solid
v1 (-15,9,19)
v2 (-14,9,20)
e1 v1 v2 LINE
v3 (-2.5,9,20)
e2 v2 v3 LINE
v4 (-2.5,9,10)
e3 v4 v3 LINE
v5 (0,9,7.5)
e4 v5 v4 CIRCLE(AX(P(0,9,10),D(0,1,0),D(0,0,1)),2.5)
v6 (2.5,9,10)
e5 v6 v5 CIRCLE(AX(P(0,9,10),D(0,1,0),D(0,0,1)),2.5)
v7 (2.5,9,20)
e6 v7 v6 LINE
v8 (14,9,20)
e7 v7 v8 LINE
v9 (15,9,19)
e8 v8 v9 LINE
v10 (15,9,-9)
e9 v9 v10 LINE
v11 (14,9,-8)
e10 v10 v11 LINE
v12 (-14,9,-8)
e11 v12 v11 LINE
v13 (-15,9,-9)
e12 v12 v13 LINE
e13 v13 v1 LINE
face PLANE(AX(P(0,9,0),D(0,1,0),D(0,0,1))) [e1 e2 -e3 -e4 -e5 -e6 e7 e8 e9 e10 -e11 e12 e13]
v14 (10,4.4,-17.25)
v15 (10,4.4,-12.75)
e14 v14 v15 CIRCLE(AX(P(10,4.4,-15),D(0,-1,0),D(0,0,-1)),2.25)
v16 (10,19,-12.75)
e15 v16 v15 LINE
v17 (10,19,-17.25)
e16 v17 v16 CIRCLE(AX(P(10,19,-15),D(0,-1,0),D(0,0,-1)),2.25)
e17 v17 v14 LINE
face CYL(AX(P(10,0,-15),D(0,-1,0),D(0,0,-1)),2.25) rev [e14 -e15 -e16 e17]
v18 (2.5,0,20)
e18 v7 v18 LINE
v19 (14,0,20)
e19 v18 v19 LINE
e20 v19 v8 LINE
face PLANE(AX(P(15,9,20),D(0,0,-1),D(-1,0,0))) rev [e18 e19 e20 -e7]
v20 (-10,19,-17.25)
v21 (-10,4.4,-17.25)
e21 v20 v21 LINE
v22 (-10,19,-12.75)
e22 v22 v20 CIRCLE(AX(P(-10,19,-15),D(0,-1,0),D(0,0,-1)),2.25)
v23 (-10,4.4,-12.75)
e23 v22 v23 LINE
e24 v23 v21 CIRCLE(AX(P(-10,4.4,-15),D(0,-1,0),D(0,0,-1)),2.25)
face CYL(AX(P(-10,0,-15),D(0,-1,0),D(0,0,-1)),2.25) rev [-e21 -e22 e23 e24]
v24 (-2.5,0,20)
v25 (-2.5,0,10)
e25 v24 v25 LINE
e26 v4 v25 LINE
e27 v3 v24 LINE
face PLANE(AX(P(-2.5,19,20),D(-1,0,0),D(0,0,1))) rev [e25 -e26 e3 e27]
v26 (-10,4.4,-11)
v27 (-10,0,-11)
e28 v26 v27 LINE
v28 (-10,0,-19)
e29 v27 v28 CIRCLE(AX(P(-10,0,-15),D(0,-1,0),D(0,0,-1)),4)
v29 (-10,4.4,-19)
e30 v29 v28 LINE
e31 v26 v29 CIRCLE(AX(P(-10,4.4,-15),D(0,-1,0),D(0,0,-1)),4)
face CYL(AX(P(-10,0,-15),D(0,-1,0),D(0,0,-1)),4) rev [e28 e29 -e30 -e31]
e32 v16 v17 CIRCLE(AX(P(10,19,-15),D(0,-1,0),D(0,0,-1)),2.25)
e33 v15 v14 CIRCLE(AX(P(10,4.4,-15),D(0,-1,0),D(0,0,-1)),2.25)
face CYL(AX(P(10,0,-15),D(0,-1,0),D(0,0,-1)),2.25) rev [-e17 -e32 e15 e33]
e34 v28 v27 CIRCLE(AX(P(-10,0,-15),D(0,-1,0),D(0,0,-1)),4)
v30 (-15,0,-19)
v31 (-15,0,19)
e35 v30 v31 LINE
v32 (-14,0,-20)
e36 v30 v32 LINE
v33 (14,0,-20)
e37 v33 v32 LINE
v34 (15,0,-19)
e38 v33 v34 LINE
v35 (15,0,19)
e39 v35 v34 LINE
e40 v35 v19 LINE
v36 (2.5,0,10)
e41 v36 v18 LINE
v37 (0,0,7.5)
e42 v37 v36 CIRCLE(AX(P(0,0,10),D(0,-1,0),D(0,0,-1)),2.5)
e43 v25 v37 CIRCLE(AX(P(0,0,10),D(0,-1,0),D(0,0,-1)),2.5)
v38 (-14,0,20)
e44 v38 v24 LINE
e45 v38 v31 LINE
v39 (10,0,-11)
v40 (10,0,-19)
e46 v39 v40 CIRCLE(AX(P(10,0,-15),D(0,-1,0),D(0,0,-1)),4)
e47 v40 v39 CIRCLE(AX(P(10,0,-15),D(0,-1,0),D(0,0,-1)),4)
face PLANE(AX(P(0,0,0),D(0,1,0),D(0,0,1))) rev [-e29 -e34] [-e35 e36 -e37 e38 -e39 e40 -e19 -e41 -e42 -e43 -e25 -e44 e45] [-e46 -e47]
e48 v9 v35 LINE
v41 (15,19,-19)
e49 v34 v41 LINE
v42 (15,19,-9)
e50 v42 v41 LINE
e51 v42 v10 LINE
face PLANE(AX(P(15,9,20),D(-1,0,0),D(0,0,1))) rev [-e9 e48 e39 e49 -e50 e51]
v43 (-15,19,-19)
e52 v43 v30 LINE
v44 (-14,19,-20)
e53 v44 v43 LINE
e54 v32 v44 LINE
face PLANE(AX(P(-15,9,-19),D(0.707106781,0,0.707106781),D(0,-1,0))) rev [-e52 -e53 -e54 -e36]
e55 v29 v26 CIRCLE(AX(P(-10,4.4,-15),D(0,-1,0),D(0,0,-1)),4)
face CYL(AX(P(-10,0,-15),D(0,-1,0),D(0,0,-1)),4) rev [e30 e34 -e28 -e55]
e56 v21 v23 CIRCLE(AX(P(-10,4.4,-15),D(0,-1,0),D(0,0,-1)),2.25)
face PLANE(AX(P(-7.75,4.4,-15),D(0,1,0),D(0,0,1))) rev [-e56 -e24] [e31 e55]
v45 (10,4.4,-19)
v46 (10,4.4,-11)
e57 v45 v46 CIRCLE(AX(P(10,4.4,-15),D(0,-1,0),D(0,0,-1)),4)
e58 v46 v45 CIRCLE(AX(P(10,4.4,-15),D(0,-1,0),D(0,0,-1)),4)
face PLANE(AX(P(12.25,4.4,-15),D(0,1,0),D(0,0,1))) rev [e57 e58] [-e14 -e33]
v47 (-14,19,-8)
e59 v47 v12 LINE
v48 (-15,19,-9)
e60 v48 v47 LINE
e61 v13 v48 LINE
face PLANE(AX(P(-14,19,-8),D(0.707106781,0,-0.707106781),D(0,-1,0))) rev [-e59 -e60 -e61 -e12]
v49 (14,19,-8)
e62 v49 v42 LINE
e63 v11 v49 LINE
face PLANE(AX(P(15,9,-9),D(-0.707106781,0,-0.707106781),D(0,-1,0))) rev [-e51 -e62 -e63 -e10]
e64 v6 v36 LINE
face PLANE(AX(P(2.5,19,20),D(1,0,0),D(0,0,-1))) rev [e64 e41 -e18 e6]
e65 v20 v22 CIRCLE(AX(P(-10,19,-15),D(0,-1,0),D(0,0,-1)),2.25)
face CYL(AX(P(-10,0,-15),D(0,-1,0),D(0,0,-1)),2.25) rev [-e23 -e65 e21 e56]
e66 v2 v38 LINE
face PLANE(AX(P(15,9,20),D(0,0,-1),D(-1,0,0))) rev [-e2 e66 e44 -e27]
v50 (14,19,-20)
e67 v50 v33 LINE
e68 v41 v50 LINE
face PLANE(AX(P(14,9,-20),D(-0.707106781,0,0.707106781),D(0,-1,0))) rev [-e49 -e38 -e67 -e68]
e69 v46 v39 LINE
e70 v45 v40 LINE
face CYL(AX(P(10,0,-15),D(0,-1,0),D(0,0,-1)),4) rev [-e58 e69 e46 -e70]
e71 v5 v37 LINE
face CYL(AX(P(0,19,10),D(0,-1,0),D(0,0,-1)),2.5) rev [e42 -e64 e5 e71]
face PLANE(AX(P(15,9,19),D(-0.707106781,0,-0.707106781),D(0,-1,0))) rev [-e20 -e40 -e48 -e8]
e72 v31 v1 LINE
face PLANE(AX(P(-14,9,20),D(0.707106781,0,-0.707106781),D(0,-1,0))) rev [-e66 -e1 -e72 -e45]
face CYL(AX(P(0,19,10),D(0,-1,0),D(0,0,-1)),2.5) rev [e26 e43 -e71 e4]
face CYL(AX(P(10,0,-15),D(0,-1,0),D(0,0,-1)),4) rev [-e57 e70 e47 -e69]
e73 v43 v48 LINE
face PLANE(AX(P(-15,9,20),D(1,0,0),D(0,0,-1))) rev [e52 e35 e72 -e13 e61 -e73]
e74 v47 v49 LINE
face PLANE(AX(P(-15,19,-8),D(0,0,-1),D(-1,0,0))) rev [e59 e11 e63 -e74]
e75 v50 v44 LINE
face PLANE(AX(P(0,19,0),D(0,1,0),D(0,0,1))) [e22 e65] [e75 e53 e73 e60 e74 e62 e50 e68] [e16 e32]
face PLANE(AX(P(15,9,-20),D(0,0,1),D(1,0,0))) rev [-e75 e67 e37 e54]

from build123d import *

# Parameters (mm, degrees)
SKETCH_1_W                   = 30
SKETCH_1_H                   = 40
EXTRUDE_1_DEPTH              = 9
SKETCH_2_W                   = 30
SKETCH_2_H                   = 12
EXTRUDE_2_DEPTH              = 10
HOLE_WIZARD_M4_1_D           = 4.5
HOLE_WIZARD_M4_1_CBORE_D     = 8
HOLE_WIZARD_M4_1_CBORE_DEPTH = 4.4
CHAMFER_1_SIZE               = 1
CUT_EXTRUDE_1_DEPTH          = 32.400636936


with BuildPart() as part:
    # 草图1 → 凸台-拉伸1 (new body)
    with BuildSketch(Plane(origin=(0, 0, 0), x_dir=(1, 0, 0), z_dir=(0, 1, 0))):
        Rectangle(SKETCH_1_W, SKETCH_1_H)
    extrude(amount=EXTRUDE_1_DEPTH)

    # 草图2 → 凸台-拉伸2 (add)
    with BuildSketch(Plane(origin=(0, 9, 0), x_dir=(1, 0, 0), z_dir=(0, 1, 0))):
        with Locations((0, 14)):
            Rectangle(SKETCH_2_W, SKETCH_2_H)
    extrude(amount=EXTRUDE_2_DEPTH)

    # M4 六角凹头螺钉的柱形沉头孔1 (through all)
    with Locations(Plane(origin=(0, 0, 0), x_dir=(-1, 0, 0), z_dir=(0, -1, 0))):
        with Locations((-10, 15), (10, 15)):
            CounterBoreHole(HOLE_WIZARD_M4_1_D / 2, HOLE_WIZARD_M4_1_CBORE_D / 2, HOLE_WIZARD_M4_1_CBORE_DEPTH)

    # 倒角1
    chamfer_1_edges = [part.edges().sort_by_distance(p)[0] for p in [
        (-15, 14, -8),
        (15, 14, -8),
        (-15, 9.5, -20),
        (15, 9.5, -20),
        (15, 4.5, 20),
        (-15, 4.5, 20),
    ]]
    chamfer(chamfer_1_edges, length=CHAMFER_1_SIZE)

    # 草图5 → 切除-拉伸1 (cut, through all)
    with BuildSketch(Plane.XZ):
        with BuildLine():
            Line((2.5, 20), (2.5, 10))
            ThreePointArc((2.5, 10), (0, 7.5), (-2.5, 10))
            Line((-2.5, 10), (-2.5, 20))
            ThreePointArc((-2.5, 20), (0, 22.5), (2.5, 20))
        make_face()
    extrude(amount=-CUT_EXTRUDE_1_DEPTH, mode=Mode.SUBTRACT)


solid = part.part
